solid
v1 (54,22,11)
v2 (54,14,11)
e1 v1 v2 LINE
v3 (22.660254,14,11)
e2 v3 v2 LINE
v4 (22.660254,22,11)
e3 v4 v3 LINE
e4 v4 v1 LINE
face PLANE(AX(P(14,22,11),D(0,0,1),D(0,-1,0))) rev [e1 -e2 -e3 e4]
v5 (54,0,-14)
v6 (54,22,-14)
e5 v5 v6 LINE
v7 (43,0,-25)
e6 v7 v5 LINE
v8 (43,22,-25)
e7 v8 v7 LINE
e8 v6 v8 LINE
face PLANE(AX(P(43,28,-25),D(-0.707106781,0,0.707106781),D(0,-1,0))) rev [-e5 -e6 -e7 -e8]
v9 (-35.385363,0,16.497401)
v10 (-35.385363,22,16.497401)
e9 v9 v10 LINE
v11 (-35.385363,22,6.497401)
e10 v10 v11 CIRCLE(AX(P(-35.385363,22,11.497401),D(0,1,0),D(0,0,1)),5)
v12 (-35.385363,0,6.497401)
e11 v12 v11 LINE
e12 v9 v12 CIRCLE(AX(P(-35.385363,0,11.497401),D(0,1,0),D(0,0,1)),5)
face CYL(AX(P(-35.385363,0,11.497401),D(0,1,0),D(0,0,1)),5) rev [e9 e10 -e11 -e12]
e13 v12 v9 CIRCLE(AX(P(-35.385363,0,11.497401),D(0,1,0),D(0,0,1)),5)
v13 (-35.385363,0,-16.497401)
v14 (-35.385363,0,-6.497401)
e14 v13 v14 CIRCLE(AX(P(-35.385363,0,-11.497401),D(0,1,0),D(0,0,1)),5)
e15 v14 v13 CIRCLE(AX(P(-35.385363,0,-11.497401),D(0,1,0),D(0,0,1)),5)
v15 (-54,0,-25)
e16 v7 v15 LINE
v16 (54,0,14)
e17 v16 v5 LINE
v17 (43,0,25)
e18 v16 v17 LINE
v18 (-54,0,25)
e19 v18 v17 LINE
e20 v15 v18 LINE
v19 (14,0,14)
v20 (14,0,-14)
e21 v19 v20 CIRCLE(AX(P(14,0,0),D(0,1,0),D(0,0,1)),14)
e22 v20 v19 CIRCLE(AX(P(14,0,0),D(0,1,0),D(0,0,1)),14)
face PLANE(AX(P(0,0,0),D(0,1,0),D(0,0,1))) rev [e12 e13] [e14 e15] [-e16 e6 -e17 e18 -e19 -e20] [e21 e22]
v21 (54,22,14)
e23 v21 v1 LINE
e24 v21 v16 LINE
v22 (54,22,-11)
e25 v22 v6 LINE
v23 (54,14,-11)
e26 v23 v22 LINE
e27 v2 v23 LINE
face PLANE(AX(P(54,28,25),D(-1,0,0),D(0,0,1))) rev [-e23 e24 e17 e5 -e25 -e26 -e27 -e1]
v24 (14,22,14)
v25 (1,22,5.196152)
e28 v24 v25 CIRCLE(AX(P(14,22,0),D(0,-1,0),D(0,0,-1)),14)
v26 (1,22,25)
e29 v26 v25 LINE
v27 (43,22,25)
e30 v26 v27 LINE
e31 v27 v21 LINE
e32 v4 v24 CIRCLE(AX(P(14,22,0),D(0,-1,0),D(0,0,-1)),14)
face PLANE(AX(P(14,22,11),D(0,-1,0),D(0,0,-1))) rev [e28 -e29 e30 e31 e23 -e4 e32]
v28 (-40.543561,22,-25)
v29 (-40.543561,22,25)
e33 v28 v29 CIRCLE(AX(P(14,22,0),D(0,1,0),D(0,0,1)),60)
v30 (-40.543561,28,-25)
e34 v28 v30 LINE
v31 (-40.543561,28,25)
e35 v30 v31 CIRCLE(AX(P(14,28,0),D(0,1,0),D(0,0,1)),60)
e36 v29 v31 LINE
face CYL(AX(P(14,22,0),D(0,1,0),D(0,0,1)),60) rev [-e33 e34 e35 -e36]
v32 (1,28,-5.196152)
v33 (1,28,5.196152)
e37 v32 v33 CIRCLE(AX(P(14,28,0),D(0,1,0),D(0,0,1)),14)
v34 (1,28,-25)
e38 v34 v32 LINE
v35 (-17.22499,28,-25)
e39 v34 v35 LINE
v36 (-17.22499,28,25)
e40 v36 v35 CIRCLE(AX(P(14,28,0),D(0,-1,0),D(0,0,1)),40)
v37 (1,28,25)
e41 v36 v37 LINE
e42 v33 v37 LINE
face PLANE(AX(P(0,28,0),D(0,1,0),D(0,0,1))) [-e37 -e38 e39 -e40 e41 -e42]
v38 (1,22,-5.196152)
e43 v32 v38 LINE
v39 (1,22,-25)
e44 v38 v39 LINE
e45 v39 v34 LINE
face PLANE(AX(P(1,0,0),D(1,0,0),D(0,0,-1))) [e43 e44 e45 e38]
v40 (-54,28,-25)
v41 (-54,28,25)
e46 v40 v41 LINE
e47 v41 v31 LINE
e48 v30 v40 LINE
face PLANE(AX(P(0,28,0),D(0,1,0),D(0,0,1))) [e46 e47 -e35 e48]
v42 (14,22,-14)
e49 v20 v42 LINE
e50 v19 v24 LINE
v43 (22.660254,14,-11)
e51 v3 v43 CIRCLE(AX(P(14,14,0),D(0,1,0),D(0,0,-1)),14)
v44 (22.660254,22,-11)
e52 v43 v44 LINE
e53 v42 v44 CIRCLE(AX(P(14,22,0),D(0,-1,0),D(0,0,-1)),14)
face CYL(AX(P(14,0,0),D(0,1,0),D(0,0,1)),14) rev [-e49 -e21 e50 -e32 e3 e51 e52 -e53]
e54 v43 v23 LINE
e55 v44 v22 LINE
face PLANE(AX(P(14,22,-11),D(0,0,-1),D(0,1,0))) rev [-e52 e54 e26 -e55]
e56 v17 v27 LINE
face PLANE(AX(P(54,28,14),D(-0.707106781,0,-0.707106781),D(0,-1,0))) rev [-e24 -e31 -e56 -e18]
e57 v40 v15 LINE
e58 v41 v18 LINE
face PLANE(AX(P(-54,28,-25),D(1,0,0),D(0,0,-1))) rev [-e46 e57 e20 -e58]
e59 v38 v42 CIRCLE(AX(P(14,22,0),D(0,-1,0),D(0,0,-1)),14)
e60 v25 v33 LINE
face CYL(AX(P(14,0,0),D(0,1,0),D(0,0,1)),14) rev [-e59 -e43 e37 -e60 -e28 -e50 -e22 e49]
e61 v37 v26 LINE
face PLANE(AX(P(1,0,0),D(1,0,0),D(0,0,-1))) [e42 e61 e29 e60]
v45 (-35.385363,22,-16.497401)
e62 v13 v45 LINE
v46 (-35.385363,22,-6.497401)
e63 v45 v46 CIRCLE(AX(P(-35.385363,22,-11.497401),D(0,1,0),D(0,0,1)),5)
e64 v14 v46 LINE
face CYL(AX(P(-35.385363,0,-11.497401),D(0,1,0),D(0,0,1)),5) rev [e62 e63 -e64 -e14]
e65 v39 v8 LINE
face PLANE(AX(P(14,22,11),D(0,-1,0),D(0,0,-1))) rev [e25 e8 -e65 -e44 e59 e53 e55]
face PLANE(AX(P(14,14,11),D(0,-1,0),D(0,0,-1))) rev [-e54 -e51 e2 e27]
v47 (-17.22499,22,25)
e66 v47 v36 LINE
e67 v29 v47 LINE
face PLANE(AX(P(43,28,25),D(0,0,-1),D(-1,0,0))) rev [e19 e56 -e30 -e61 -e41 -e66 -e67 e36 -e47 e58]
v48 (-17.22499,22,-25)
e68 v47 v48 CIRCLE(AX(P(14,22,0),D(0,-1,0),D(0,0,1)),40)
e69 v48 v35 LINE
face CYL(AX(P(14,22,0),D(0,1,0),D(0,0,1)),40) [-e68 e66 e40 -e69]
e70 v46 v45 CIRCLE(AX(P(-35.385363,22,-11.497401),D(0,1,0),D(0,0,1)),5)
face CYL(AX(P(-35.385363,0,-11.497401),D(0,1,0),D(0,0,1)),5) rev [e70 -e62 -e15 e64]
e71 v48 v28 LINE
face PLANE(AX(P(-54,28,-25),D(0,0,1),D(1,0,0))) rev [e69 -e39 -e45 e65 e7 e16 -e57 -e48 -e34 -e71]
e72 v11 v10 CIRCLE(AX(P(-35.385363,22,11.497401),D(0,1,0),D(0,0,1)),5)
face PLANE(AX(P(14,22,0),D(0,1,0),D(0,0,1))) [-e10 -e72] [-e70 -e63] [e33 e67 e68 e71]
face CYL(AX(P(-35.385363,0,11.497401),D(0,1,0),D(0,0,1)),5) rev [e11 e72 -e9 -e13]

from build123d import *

# Parameters (mm, degrees)
BASE_BLOCK_108X50X28_DEPTH     = 28
JAW_SLOT_PROFILE_W             = 22
JAW_SLOT_PROFILE_H             = 6
JAW_SLOT_CUT_DEPTH             = 40
BORE_28_PROFILE_R              = 14
BORE_28_DEPTH                  = 66.76473219
THROUGH_SLOT_CUT_DEPTH         = 53
SIDE_GROOVE_PROFILE_W          = 22
SIDE_GROOVE_PROFILE_H          = 8
SIDE_GROOVE_CUT_DEPTH          = 40
END_CHAMFER_11X45_SIZE         = 11
ARC_RECESS_6_DEEP_DEPTH        = 6
ARC_POCKET_AND_HOLES_PROFILE_R = 5
ARC_POCKET_AND_HOLES_CUT_DEPTH = 66.76473219


with BuildPart() as part:
    # Base Block Profile → Base Block 108x50x28 (new body)
    with BuildSketch(Plane(origin=(0, 0, 0), x_dir=(1, 0, 0), z_dir=(0, 1, 0))):
        Polygon((-54, 25), (43, 25), (54, 25), (54, -25), (43, -25), (-54, -25), align=None)
    extrude(amount=BASE_BLOCK_108X50X28_DEPTH)

    # Jaw Slot Profile → Jaw Slot Cut (cut)
    with BuildSketch(Plane(origin=(54, 0, 0), x_dir=(0, 0, -1), z_dir=(1, 0, 0))):
        with Locations((0, 25)):
            Rectangle(JAW_SLOT_PROFILE_W, JAW_SLOT_PROFILE_H)
    extrude(amount=-JAW_SLOT_CUT_DEPTH, mode=Mode.SUBTRACT)

    # Bore Ø28 Profile → Bore Ø28 (cut, through all)
    with BuildSketch(Plane(origin=(0, 28, 0), x_dir=(1, 0, 0), z_dir=(0, 1, 0))):
        with Locations(Location((14, 0, 0), (0, 0, 270))):
            Circle(BORE_28_PROFILE_R)
    extrude(amount=-BORE_28_DEPTH, mode=Mode.SUBTRACT)

    # Through Slot Profile → Through Slot Cut (cut)
    with BuildSketch(Plane(origin=(54, 0, 0), x_dir=(0, 0, -1), z_dir=(1, 0, 0))):
        Polygon((-25, 28), (-11, 28), (25, 28), (25, 22), (-11, 22), (-25, 22), align=None)
    extrude(amount=-THROUGH_SLOT_CUT_DEPTH, mode=Mode.SUBTRACT)

    # Side Groove Profile → Side Groove Cut (cut)
    with BuildSketch(Plane(origin=(54, 0, 0), x_dir=(0, 0, -1), z_dir=(1, 0, 0))):
        with Locations((0, 18)):
            Rectangle(SIDE_GROOVE_PROFILE_W, SIDE_GROOVE_PROFILE_H)
    extrude(amount=-SIDE_GROOVE_CUT_DEPTH, mode=Mode.SUBTRACT)

    # End Chamfer 11x45°
    end_chamfer_11x45_edges = [part.edges().sort_by_distance(p)[0] for p in [
        (54, 11, 25),
        (54, 11, -25),
    ]]
    chamfer(end_chamfer_11x45_edges, length=END_CHAMFER_11X45_SIZE)

    # Arc Recess Profile → Arc Recess 6 Deep (cut)
    with BuildSketch(Plane(origin=(0, 28, 0), x_dir=(1, 0, 0), z_dir=(0, 1, 0))):
        with BuildLine():
            Line((-40.543560573, -25), (-17.224989992, -25))
            ThreePointArc((-17.224989992, -25), (-26, 0), (-17.224989992, 25))
            Line((-17.224989992, 25), (-40.543560573, 25))
            ThreePointArc((-40.543560573, 25), (-46, 0), (-40.543560573, -25))
        make_face()
    extrude(amount=-ARC_RECESS_6_DEEP_DEPTH, mode=Mode.SUBTRACT)

    # Arc Pocket and Holes Profile → Arc Pocket and Holes Cut (cut, through all)
    with BuildSketch(Plane(origin=(0, 28, 0), x_dir=(1, 0, 0), z_dir=(0, 1, 0))):
        with Locations(Location((-35.385362758, 11.497401318, 0), (0, 0, 270))):
            Circle(ARC_POCKET_AND_HOLES_PROFILE_R)
        with Locations(Location((-35.385362758, -11.497401318, 0), (0, 0, 270))):
            Circle(ARC_POCKET_AND_HOLES_PROFILE_R)
    extrude(amount=-ARC_POCKET_AND_HOLES_CUT_DEPTH, mode=Mode.SUBTRACT)


solid = part.part
